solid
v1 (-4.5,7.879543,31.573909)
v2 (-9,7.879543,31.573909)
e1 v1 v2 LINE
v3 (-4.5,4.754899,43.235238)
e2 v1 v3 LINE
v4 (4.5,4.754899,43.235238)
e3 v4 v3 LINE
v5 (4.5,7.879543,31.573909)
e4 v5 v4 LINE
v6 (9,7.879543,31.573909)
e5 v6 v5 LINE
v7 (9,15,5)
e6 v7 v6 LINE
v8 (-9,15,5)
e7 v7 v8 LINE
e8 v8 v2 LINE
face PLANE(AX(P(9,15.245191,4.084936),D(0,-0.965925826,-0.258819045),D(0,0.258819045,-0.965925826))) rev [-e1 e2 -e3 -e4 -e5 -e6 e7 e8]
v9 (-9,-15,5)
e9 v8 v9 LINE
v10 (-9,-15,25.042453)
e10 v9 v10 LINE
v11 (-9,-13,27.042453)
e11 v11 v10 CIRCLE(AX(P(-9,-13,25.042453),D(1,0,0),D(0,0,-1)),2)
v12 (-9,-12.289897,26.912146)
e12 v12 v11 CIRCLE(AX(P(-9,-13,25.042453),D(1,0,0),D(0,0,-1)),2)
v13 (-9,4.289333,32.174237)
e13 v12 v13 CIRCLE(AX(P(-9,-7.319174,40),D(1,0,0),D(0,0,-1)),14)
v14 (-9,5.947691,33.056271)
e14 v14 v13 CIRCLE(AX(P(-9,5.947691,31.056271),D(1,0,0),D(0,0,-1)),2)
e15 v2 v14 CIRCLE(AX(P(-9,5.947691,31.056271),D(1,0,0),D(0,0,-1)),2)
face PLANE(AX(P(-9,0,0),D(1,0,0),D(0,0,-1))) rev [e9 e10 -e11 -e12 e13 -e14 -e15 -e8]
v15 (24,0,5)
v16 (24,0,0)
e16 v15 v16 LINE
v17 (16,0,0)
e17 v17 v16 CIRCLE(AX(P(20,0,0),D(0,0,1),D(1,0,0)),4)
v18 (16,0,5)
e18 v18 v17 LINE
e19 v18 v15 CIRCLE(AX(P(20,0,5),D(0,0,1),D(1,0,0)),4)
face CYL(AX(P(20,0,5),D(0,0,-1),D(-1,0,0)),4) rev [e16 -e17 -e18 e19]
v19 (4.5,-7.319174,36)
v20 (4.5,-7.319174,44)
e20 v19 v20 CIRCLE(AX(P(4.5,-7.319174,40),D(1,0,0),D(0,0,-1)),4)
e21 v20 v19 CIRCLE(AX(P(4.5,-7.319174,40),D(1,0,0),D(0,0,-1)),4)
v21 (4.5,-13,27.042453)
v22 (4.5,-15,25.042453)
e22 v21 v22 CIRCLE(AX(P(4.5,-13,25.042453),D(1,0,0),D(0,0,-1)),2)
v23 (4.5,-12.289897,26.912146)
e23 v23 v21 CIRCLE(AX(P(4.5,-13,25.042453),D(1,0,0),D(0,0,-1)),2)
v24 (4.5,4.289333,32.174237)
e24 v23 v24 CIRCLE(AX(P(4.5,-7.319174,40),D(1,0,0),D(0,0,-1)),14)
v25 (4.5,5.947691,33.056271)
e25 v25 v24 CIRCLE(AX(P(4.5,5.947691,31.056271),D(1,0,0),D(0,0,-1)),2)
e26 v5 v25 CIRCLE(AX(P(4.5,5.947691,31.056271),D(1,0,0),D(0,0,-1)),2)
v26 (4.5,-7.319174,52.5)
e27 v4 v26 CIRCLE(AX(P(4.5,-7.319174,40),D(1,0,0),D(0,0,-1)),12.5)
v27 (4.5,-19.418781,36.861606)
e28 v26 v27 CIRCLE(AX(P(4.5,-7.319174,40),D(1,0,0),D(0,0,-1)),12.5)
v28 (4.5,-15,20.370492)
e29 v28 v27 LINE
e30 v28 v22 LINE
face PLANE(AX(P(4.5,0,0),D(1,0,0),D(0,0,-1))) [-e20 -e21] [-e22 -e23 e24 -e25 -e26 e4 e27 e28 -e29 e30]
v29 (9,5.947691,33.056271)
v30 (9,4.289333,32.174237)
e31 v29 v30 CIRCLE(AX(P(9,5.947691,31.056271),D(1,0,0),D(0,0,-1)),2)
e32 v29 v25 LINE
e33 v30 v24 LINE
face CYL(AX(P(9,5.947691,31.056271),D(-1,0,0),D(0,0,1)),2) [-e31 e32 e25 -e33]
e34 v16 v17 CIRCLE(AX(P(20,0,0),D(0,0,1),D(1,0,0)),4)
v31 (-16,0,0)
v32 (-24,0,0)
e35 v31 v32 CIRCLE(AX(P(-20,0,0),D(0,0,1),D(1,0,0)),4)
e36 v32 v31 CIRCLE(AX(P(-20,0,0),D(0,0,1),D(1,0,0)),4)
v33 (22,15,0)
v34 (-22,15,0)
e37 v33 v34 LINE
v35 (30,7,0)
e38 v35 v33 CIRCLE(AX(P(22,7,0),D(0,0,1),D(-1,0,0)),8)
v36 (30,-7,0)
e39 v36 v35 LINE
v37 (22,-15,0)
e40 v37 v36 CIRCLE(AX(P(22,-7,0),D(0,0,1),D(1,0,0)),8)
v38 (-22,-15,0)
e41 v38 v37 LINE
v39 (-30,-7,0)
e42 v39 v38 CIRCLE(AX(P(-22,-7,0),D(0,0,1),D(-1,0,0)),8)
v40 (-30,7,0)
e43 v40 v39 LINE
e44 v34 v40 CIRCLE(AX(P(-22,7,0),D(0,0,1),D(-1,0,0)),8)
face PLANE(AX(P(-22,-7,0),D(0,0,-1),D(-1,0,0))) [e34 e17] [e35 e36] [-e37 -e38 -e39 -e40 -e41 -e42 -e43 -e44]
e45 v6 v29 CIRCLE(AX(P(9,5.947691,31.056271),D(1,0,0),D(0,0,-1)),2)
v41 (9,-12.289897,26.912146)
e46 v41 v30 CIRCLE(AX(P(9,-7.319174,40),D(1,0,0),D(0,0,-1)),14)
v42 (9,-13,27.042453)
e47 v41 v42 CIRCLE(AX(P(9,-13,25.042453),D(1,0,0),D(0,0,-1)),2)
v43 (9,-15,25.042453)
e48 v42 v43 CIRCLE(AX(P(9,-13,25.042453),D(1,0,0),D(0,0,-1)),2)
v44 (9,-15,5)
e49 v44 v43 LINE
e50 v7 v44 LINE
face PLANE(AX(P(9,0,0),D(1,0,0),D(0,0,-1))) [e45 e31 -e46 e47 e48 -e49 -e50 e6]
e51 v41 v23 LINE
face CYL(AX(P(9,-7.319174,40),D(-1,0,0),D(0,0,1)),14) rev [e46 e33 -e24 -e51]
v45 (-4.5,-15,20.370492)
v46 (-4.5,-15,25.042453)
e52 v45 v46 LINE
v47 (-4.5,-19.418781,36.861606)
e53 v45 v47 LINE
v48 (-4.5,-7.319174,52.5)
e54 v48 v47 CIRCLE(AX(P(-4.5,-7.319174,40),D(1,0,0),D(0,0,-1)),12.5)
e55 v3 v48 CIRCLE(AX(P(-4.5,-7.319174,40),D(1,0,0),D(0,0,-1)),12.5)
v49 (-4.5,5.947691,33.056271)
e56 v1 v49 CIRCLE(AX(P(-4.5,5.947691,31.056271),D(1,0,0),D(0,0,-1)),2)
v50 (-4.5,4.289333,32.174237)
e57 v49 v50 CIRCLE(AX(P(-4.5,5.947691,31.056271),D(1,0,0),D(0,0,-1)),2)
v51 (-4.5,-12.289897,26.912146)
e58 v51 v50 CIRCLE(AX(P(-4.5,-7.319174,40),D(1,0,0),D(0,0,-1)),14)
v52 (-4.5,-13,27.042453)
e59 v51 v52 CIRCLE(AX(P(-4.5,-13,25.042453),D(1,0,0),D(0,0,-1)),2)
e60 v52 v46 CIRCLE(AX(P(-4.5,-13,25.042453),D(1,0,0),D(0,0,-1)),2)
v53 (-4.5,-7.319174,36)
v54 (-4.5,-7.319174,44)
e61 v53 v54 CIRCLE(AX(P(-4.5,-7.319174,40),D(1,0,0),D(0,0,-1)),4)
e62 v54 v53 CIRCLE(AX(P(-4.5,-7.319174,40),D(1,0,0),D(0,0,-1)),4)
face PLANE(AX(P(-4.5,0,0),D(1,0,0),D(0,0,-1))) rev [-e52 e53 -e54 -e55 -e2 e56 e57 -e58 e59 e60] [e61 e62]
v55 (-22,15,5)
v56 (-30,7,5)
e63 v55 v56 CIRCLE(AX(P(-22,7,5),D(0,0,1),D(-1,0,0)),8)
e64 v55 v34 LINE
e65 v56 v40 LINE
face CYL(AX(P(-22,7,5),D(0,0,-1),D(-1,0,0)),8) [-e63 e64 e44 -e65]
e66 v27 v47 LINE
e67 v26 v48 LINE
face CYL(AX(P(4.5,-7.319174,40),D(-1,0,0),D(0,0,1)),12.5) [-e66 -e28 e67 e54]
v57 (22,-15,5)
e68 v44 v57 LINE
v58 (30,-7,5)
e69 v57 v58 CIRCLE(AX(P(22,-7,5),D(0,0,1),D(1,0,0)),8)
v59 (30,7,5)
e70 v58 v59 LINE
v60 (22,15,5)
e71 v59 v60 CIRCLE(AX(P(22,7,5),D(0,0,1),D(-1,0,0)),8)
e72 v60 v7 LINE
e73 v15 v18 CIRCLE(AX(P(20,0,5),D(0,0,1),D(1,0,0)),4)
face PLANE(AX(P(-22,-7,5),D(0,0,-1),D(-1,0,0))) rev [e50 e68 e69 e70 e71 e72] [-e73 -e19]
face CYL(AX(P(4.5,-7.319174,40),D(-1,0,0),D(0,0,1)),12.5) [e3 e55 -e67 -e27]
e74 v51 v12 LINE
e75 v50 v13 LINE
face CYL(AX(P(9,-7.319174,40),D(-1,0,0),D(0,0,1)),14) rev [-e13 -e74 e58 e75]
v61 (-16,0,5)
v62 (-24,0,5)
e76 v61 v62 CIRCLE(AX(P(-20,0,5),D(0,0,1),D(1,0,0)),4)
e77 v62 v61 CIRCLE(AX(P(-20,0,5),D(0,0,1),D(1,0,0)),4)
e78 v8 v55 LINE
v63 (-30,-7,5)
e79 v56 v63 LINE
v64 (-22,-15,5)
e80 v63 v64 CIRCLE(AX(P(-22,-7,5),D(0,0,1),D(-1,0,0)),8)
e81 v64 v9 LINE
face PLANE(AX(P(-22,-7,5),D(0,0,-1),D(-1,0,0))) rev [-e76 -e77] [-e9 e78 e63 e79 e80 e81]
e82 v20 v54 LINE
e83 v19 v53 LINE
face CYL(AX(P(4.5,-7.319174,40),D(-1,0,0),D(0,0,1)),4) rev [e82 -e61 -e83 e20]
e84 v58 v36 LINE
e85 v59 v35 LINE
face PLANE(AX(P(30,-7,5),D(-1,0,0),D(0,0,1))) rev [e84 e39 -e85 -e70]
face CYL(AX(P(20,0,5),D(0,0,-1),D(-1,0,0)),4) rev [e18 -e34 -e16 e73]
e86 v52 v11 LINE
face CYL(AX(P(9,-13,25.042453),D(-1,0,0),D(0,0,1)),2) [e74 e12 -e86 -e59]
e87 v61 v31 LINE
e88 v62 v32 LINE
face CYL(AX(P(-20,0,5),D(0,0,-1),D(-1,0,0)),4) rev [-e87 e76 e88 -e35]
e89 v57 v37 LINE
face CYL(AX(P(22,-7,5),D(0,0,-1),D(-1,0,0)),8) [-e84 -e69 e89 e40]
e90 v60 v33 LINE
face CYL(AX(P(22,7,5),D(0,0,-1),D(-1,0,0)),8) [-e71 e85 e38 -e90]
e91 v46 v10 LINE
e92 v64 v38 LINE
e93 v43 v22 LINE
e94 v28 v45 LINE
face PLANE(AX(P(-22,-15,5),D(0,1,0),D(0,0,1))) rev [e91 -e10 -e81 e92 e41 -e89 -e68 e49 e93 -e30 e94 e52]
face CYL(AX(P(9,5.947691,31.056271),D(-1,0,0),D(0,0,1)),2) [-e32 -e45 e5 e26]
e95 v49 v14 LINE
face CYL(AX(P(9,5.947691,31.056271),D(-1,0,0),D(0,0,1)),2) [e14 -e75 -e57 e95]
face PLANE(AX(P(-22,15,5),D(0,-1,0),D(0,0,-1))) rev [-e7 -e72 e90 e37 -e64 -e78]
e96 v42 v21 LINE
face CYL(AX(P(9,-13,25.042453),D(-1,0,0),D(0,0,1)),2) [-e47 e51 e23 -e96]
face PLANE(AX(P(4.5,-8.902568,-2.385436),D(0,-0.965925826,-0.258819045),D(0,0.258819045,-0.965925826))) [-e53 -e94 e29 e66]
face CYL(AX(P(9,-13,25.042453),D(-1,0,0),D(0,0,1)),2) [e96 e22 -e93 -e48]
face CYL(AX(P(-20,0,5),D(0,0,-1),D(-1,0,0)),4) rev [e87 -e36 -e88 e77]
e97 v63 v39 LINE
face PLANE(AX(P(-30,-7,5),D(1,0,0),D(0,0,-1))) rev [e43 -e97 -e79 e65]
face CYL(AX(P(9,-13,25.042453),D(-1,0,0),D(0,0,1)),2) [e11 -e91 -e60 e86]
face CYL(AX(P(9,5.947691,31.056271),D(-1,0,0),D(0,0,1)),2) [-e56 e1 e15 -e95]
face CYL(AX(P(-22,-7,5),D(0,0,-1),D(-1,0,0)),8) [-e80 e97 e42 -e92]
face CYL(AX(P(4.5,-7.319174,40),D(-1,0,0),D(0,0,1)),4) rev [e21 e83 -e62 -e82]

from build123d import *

# Parameters (mm, degrees)
BASE_PLATE_SKETCH_R   = 4
BASE_PLATE_DEPTH      = 5
LUG_PROFILE_SKETCH_R  = 4
LUG_SUPPORT_WEB_DEPTH = 4.5
LUG_EYE_DEPTH         = 9


with BuildPart() as part:
    # Base Plate Sketch → Base Plate (new body)
    with BuildSketch(Plane.XY):
        with BuildLine():
            Line((-22, -15), (22, -15))
            ThreePointArc((22, -15), (27.656854249, -12.656854249), (30, -7))
            Line((30, -7), (30, 7))
            ThreePointArc((30, 7), (27.656854249, 12.656854249), (22, 15))
            Line((22, 15), (-22, 15))
            ThreePointArc((-22, 15), (-27.656854249, 12.656854249), (-30, 7))
            Line((-30, 7), (-30, -7))
            ThreePointArc((-30, -7), (-27.656854249, -12.656854249), (-22, -15))
        make_face()
        with Locations((20, 0)):
            Circle(BASE_PLATE_SKETCH_R, mode=Mode.SUBTRACT)
        with Locations((-20, 0)):
            Circle(BASE_PLATE_SKETCH_R, mode=Mode.SUBTRACT)
    extrude(amount=BASE_PLATE_DEPTH)



with BuildPart() as body_2:
    # Lug Profile Sketch → Lug Support Web (new, symmetric)
    with BuildSketch(Plane(origin=(0, 0, 0), x_dir=(0, 0, -1), z_dir=(1, 0, 0))):
        with BuildLine():
            ThreePointArc((-32.17423683, 4.289332839), (-33.028883618, 6.27753657), (-31.573908753, 7.87954261))
            Line((-31.573908753, 7.87954261), (-43.235238064, 4.754898838))
            ThreePointArc((-43.235238064, 4.754898838), (-52.086936749, -10.506015692), (-36.861605806, -19.418780673))
            Line((-36.861605806, -19.418780673), (-36.668125757, -19.36693785))
            Line((-36.668125757, -19.36693785), (-20.370491826, -15))
            Line((-20.370491826, -15), (-25.04245288, -15))
            ThreePointArc((-25.04245288, -15), (-26.688692003, -14.135736214), (-26.91214627, -12.289896749))
            ThreePointArc((-26.91214627, -12.289896749), (-26.655991742, -3.083912061), (-32.17423683, 4.289332839))
        make_face()
        with Locations((-40, -7.31917399)):
            Circle(LUG_PROFILE_SKETCH_R, mode=Mode.SUBTRACT)
    extrude(amount=LUG_SUPPORT_WEB_DEPTH, both=True)


with BuildPart() as part_1:
    add(part.part)

    add(body_2.part)  # Lug Eye merges body 2
    # Sketch4_3 → Lug Eye (add, symmetric)
    with BuildSketch(Plane(origin=(0, 0, 0), x_dir=(0, 0, -1), z_dir=(1, 0, 0))):
        with BuildLine():
            Line((-5, -15), (-5, 15))
            Line((-5, 15), (-31.573908753, 7.87954261))
            ThreePointArc((-31.573908753, 7.87954261), (-33.028883618, 6.27753657), (-32.17423683, 4.289332839))
            ThreePointArc((-32.17423683, 4.289332839), (-26.655991742, -3.083912061), (-26.91214627, -12.289896749))
            ThreePointArc((-26.91214627, -12.289896749), (-26.688692003, -14.135736214), (-25.04245288, -15))
            Line((-25.04245288, -15), (-20.370491826, -15))
            Line((-20.370491826, -15), (-5, -15))
        make_face()
    extrude(amount=LUG_EYE_DEPTH, both=True)


solid = part_1.part
